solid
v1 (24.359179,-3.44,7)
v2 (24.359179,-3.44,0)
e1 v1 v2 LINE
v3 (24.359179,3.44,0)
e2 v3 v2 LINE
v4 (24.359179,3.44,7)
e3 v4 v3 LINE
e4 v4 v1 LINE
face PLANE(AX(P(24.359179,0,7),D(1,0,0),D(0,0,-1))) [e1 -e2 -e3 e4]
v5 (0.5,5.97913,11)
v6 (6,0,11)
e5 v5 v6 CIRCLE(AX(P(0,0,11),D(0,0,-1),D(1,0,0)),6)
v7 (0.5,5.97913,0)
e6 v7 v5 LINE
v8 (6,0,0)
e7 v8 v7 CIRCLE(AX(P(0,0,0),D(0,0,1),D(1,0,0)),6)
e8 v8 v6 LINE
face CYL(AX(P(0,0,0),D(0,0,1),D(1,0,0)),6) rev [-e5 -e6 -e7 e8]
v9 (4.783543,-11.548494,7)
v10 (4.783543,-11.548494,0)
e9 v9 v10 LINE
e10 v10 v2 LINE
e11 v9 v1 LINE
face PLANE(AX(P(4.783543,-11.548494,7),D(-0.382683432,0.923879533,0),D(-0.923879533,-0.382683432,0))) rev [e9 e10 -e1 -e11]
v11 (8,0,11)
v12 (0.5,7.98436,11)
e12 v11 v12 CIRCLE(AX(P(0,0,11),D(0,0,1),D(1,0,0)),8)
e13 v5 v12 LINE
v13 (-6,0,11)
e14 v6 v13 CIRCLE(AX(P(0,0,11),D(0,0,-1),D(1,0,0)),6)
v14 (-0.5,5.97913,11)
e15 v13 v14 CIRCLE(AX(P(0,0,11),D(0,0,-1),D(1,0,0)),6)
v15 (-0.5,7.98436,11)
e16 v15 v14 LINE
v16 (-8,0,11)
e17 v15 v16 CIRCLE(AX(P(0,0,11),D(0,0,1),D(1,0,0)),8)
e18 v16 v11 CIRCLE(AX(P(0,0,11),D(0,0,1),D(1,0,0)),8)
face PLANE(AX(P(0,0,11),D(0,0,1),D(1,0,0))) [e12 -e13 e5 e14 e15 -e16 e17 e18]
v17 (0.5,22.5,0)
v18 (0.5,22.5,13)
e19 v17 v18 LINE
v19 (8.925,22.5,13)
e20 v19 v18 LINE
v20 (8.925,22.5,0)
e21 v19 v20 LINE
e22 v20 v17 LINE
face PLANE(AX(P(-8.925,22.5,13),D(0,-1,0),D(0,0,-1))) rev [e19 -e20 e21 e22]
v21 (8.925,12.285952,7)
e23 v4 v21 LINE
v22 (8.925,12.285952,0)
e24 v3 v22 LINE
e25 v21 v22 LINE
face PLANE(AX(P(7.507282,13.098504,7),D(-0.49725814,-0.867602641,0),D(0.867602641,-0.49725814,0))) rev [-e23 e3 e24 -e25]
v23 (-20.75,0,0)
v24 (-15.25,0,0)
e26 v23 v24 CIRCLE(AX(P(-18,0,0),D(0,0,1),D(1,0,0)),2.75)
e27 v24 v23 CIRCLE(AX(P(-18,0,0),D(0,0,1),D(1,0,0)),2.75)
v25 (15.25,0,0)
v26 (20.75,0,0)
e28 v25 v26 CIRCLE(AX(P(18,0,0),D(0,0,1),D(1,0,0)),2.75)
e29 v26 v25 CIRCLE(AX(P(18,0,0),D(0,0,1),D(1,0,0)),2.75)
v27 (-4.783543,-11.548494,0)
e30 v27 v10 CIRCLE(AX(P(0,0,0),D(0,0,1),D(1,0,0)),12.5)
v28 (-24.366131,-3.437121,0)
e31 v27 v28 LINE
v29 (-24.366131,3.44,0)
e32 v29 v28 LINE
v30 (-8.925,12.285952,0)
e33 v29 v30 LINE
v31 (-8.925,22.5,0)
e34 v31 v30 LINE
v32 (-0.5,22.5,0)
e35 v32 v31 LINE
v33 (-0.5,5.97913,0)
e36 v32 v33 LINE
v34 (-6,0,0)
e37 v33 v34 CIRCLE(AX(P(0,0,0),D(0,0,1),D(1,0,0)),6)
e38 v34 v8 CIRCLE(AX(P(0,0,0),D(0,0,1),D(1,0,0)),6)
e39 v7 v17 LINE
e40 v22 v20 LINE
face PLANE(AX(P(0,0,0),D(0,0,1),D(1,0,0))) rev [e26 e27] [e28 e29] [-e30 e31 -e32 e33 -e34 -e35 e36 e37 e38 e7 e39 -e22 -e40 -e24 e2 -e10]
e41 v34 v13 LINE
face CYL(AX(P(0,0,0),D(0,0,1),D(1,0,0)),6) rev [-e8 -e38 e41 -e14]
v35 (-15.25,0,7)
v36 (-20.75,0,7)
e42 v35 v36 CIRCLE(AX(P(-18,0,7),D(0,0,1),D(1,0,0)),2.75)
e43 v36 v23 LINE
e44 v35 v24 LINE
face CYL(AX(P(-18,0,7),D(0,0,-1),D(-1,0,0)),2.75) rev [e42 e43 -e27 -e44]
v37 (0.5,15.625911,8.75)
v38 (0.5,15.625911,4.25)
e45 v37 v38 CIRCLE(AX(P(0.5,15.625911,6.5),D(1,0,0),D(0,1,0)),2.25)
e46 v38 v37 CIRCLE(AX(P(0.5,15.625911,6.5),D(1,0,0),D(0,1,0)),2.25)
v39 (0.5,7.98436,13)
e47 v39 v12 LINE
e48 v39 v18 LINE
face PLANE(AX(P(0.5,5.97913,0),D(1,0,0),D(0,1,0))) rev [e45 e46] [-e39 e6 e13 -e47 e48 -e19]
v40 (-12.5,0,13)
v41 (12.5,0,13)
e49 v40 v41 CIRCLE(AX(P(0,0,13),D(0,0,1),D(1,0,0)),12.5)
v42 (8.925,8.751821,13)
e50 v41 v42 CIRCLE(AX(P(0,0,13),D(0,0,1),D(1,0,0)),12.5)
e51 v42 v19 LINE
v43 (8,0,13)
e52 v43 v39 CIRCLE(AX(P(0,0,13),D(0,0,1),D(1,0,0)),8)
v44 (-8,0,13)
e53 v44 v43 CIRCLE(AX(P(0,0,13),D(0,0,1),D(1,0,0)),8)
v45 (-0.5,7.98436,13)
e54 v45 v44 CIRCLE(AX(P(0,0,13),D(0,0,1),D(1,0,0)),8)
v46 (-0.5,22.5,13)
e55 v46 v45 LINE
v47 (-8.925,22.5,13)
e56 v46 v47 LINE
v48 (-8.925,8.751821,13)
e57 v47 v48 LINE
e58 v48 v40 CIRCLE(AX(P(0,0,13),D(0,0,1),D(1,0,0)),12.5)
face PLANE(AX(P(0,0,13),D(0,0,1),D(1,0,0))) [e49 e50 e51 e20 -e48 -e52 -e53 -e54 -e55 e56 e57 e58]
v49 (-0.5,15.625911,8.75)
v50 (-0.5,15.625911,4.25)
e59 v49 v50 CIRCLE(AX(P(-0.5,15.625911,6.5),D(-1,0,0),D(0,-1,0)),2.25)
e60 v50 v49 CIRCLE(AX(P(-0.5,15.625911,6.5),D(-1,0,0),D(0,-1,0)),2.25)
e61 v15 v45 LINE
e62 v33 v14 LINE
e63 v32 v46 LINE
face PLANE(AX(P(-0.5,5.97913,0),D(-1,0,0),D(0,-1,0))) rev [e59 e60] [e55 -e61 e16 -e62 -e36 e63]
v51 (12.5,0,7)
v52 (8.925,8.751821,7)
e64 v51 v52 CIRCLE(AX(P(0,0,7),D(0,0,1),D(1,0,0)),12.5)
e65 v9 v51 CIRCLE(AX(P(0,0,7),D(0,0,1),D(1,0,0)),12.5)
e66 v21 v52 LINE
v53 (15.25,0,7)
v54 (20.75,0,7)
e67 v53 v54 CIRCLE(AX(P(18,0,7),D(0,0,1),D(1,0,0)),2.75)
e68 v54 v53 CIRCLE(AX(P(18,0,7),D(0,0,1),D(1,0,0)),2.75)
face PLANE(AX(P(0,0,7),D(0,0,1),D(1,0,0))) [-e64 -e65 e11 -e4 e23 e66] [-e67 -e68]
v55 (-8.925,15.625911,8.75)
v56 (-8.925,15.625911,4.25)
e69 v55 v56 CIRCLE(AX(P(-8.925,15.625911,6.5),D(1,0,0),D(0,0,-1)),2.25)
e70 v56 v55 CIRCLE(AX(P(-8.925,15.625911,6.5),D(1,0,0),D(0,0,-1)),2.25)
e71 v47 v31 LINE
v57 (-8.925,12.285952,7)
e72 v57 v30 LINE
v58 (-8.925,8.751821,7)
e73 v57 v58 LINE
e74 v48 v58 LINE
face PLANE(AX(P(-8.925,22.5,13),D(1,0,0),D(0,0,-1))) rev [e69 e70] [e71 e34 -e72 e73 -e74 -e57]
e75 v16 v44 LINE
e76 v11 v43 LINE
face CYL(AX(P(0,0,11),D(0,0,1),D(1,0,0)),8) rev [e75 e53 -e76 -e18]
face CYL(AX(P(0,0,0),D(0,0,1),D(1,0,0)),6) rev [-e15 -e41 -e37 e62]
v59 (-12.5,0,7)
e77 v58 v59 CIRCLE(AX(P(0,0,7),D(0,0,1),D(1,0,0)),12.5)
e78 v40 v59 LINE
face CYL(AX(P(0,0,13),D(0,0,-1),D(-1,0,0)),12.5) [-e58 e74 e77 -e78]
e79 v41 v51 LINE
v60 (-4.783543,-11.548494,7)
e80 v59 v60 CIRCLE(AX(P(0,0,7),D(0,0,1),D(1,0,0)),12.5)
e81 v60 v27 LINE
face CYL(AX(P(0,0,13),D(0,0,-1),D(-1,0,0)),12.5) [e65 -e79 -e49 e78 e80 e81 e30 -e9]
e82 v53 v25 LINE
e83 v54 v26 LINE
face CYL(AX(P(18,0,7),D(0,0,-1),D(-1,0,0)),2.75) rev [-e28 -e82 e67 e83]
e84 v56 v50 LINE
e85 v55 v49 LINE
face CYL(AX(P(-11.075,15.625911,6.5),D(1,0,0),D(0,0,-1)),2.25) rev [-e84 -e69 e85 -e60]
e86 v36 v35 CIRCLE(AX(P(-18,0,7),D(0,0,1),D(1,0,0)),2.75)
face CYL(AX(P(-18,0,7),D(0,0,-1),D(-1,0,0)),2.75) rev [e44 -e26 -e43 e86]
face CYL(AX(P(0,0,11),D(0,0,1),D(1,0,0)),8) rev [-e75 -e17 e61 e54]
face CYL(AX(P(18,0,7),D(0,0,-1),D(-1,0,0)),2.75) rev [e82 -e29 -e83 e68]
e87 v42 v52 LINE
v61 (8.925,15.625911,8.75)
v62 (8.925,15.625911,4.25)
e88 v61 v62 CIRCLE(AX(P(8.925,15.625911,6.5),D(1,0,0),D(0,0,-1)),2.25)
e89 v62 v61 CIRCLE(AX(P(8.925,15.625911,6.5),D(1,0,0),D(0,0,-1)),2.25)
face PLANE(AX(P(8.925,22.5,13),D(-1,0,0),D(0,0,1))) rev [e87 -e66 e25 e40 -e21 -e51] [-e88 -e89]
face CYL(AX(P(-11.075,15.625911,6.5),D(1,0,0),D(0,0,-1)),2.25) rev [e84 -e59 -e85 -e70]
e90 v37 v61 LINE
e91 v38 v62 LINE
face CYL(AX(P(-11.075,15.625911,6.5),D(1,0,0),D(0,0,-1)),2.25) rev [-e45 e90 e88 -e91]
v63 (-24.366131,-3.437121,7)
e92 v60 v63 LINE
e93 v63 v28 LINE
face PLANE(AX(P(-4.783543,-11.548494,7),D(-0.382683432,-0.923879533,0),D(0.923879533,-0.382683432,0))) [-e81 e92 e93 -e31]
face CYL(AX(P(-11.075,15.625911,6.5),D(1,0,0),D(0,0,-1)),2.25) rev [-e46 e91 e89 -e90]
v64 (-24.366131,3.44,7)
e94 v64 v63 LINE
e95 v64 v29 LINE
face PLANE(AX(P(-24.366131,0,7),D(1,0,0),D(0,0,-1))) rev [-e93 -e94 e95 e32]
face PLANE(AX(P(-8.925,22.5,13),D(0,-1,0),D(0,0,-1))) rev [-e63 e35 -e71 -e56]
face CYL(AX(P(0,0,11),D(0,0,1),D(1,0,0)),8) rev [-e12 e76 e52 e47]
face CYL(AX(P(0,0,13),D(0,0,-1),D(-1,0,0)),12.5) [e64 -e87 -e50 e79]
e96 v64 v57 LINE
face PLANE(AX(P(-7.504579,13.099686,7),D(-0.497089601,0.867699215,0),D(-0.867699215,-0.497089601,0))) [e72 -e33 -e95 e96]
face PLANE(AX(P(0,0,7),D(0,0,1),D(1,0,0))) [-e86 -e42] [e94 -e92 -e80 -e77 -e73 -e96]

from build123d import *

# Parameters (mm, degrees)
CLAMP_RING_SKETCH_R          = 12.5
CLAMP_RING_25_DEPTH          = 13
CLAMP_BLOCK_DEPTH            = 13
BORE_SKETCH_R                = 6
BORE_12_DEPTH                = 13
COUNTERBORE_SKETCH_R         = 8
COUNTERBORE_16X2_DEPTH       = 2
MOUNTING_FLANGE_SKETCH_R     = 2.75
MOUNTING_FLANGE_2X_5_5_DEPTH = 7
CLAMP_SPLIT_SLOT_DEPTH       = 36.622441552
CLAMP_SCREW_HOLE_SKETCH_R    = 2.25
CLAMP_SCREW_HOLE_4_5_DEPTH   = 20


with BuildPart() as part:
    # Clamp Ring Sketch → Clamp Ring Ø25 (new body)
    with BuildSketch(Plane.XY):
        with Locations(Location((0, 0, 0), (0, 0, 180))):
            Circle(CLAMP_RING_SKETCH_R)
    extrude(amount=CLAMP_RING_25_DEPTH)

    # Clamp Block Sketch → Clamp Block (add)
    with BuildSketch(Plane.XY):
        with BuildLine():
            Line((-8.925, 22.5), (8.925, 22.5))
            Line((8.925, 22.5), (8.925, 8.751821239))
            ThreePointArc((8.925, 8.751821239), (0, 12.5), (-8.925, 8.751821239))
            Line((-8.925, 8.751821239), (-8.925, 22.5))
        make_face()
    extrude(amount=CLAMP_BLOCK_DEPTH)

    # Bore Sketch → Bore Ø12 (cut)
    with BuildSketch(Plane.XY.offset(13)):
        Circle(BORE_SKETCH_R)
    extrude(amount=-BORE_12_DEPTH, mode=Mode.SUBTRACT)

    # Counterbore Sketch → Counterbore Ø16x2 (cut)
    with BuildSketch(Plane.XY.offset(13)):
        Circle(COUNTERBORE_SKETCH_R)
    extrude(amount=-COUNTERBORE_16X2_DEPTH, mode=Mode.SUBTRACT)

    # Mounting Flange Sketch → Mounting Flange 2xØ5.5 (add)
    # profile 1 of 2: a face of its own
    with BuildSketch(Plane.XY):
        with BuildLine():
            Line((-8.925, 12.285952074), (-24.366131046, 3.44))
            Line((-24.366131046, 3.44), (-24.366131046, -3.437120562))
            Line((-24.366131046, -3.437120562), (-4.783542905, -11.548494156))
            ThreePointArc((-4.783542905, -11.548494156), (-12.247723806, -2.498651951), (-8.925, 8.751821239))
            Line((-8.925, 8.751821239), (-8.925, 12.285952074))
        make_face()
        with Locations((-18, 0)):
            Circle(MOUNTING_FLANGE_SKETCH_R, mode=Mode.SUBTRACT)
    # profile 2 of 2: a face of its own
    with BuildSketch(Plane.XY):
        with BuildLine():
            ThreePointArc((8.925, 8.751821239), (12.247723806, -2.498651951), (4.783542905, -11.548494156))
            Line((4.783542905, -11.548494156), (24.359179467, -3.44))
            Line((24.359179467, -3.44), (24.359179467, 3.44))
            Line((24.359179467, 3.44), (8.925, 12.285952074))
            Line((8.925, 12.285952074), (8.925, 8.751821239))
        make_face()
        with Locations((18, 0)):
            Circle(MOUNTING_FLANGE_SKETCH_R, mode=Mode.SUBTRACT)
    extrude(amount=MOUNTING_FLANGE_2X_5_5_DEPTH)

    # Split Slot Sketch → Clamp Split Slot (cut, through all)
    with BuildSketch(Plane.XY.offset(13)):
        with BuildLine():
            Line((0.5, 5.979130372), (0.5, 22.5))
            Line((0.5, 22.5), (-0.5, 22.5))
            Line((-0.5, 22.5), (-0.5, 5.979130372))
            ThreePointArc((-0.5, 5.979130372), (0, 6), (0.5, 5.979130372))
        make_face()
    extrude(amount=-CLAMP_SPLIT_SLOT_DEPTH, mode=Mode.SUBTRACT)

    # Clamp Screw Hole Sketch → Clamp Screw Hole Ø4.5 (cut)
    with BuildSketch(Plane(origin=(8.925, 0, 0), x_dir=(0, 0, -1), z_dir=(1, 0, 0))):
        with Locations((-6.5, 15.62591062)):
            Circle(CLAMP_SCREW_HOLE_SKETCH_R)
    extrude(amount=-CLAMP_SCREW_HOLE_4_5_DEPTH, mode=Mode.SUBTRACT)


solid = part.part
